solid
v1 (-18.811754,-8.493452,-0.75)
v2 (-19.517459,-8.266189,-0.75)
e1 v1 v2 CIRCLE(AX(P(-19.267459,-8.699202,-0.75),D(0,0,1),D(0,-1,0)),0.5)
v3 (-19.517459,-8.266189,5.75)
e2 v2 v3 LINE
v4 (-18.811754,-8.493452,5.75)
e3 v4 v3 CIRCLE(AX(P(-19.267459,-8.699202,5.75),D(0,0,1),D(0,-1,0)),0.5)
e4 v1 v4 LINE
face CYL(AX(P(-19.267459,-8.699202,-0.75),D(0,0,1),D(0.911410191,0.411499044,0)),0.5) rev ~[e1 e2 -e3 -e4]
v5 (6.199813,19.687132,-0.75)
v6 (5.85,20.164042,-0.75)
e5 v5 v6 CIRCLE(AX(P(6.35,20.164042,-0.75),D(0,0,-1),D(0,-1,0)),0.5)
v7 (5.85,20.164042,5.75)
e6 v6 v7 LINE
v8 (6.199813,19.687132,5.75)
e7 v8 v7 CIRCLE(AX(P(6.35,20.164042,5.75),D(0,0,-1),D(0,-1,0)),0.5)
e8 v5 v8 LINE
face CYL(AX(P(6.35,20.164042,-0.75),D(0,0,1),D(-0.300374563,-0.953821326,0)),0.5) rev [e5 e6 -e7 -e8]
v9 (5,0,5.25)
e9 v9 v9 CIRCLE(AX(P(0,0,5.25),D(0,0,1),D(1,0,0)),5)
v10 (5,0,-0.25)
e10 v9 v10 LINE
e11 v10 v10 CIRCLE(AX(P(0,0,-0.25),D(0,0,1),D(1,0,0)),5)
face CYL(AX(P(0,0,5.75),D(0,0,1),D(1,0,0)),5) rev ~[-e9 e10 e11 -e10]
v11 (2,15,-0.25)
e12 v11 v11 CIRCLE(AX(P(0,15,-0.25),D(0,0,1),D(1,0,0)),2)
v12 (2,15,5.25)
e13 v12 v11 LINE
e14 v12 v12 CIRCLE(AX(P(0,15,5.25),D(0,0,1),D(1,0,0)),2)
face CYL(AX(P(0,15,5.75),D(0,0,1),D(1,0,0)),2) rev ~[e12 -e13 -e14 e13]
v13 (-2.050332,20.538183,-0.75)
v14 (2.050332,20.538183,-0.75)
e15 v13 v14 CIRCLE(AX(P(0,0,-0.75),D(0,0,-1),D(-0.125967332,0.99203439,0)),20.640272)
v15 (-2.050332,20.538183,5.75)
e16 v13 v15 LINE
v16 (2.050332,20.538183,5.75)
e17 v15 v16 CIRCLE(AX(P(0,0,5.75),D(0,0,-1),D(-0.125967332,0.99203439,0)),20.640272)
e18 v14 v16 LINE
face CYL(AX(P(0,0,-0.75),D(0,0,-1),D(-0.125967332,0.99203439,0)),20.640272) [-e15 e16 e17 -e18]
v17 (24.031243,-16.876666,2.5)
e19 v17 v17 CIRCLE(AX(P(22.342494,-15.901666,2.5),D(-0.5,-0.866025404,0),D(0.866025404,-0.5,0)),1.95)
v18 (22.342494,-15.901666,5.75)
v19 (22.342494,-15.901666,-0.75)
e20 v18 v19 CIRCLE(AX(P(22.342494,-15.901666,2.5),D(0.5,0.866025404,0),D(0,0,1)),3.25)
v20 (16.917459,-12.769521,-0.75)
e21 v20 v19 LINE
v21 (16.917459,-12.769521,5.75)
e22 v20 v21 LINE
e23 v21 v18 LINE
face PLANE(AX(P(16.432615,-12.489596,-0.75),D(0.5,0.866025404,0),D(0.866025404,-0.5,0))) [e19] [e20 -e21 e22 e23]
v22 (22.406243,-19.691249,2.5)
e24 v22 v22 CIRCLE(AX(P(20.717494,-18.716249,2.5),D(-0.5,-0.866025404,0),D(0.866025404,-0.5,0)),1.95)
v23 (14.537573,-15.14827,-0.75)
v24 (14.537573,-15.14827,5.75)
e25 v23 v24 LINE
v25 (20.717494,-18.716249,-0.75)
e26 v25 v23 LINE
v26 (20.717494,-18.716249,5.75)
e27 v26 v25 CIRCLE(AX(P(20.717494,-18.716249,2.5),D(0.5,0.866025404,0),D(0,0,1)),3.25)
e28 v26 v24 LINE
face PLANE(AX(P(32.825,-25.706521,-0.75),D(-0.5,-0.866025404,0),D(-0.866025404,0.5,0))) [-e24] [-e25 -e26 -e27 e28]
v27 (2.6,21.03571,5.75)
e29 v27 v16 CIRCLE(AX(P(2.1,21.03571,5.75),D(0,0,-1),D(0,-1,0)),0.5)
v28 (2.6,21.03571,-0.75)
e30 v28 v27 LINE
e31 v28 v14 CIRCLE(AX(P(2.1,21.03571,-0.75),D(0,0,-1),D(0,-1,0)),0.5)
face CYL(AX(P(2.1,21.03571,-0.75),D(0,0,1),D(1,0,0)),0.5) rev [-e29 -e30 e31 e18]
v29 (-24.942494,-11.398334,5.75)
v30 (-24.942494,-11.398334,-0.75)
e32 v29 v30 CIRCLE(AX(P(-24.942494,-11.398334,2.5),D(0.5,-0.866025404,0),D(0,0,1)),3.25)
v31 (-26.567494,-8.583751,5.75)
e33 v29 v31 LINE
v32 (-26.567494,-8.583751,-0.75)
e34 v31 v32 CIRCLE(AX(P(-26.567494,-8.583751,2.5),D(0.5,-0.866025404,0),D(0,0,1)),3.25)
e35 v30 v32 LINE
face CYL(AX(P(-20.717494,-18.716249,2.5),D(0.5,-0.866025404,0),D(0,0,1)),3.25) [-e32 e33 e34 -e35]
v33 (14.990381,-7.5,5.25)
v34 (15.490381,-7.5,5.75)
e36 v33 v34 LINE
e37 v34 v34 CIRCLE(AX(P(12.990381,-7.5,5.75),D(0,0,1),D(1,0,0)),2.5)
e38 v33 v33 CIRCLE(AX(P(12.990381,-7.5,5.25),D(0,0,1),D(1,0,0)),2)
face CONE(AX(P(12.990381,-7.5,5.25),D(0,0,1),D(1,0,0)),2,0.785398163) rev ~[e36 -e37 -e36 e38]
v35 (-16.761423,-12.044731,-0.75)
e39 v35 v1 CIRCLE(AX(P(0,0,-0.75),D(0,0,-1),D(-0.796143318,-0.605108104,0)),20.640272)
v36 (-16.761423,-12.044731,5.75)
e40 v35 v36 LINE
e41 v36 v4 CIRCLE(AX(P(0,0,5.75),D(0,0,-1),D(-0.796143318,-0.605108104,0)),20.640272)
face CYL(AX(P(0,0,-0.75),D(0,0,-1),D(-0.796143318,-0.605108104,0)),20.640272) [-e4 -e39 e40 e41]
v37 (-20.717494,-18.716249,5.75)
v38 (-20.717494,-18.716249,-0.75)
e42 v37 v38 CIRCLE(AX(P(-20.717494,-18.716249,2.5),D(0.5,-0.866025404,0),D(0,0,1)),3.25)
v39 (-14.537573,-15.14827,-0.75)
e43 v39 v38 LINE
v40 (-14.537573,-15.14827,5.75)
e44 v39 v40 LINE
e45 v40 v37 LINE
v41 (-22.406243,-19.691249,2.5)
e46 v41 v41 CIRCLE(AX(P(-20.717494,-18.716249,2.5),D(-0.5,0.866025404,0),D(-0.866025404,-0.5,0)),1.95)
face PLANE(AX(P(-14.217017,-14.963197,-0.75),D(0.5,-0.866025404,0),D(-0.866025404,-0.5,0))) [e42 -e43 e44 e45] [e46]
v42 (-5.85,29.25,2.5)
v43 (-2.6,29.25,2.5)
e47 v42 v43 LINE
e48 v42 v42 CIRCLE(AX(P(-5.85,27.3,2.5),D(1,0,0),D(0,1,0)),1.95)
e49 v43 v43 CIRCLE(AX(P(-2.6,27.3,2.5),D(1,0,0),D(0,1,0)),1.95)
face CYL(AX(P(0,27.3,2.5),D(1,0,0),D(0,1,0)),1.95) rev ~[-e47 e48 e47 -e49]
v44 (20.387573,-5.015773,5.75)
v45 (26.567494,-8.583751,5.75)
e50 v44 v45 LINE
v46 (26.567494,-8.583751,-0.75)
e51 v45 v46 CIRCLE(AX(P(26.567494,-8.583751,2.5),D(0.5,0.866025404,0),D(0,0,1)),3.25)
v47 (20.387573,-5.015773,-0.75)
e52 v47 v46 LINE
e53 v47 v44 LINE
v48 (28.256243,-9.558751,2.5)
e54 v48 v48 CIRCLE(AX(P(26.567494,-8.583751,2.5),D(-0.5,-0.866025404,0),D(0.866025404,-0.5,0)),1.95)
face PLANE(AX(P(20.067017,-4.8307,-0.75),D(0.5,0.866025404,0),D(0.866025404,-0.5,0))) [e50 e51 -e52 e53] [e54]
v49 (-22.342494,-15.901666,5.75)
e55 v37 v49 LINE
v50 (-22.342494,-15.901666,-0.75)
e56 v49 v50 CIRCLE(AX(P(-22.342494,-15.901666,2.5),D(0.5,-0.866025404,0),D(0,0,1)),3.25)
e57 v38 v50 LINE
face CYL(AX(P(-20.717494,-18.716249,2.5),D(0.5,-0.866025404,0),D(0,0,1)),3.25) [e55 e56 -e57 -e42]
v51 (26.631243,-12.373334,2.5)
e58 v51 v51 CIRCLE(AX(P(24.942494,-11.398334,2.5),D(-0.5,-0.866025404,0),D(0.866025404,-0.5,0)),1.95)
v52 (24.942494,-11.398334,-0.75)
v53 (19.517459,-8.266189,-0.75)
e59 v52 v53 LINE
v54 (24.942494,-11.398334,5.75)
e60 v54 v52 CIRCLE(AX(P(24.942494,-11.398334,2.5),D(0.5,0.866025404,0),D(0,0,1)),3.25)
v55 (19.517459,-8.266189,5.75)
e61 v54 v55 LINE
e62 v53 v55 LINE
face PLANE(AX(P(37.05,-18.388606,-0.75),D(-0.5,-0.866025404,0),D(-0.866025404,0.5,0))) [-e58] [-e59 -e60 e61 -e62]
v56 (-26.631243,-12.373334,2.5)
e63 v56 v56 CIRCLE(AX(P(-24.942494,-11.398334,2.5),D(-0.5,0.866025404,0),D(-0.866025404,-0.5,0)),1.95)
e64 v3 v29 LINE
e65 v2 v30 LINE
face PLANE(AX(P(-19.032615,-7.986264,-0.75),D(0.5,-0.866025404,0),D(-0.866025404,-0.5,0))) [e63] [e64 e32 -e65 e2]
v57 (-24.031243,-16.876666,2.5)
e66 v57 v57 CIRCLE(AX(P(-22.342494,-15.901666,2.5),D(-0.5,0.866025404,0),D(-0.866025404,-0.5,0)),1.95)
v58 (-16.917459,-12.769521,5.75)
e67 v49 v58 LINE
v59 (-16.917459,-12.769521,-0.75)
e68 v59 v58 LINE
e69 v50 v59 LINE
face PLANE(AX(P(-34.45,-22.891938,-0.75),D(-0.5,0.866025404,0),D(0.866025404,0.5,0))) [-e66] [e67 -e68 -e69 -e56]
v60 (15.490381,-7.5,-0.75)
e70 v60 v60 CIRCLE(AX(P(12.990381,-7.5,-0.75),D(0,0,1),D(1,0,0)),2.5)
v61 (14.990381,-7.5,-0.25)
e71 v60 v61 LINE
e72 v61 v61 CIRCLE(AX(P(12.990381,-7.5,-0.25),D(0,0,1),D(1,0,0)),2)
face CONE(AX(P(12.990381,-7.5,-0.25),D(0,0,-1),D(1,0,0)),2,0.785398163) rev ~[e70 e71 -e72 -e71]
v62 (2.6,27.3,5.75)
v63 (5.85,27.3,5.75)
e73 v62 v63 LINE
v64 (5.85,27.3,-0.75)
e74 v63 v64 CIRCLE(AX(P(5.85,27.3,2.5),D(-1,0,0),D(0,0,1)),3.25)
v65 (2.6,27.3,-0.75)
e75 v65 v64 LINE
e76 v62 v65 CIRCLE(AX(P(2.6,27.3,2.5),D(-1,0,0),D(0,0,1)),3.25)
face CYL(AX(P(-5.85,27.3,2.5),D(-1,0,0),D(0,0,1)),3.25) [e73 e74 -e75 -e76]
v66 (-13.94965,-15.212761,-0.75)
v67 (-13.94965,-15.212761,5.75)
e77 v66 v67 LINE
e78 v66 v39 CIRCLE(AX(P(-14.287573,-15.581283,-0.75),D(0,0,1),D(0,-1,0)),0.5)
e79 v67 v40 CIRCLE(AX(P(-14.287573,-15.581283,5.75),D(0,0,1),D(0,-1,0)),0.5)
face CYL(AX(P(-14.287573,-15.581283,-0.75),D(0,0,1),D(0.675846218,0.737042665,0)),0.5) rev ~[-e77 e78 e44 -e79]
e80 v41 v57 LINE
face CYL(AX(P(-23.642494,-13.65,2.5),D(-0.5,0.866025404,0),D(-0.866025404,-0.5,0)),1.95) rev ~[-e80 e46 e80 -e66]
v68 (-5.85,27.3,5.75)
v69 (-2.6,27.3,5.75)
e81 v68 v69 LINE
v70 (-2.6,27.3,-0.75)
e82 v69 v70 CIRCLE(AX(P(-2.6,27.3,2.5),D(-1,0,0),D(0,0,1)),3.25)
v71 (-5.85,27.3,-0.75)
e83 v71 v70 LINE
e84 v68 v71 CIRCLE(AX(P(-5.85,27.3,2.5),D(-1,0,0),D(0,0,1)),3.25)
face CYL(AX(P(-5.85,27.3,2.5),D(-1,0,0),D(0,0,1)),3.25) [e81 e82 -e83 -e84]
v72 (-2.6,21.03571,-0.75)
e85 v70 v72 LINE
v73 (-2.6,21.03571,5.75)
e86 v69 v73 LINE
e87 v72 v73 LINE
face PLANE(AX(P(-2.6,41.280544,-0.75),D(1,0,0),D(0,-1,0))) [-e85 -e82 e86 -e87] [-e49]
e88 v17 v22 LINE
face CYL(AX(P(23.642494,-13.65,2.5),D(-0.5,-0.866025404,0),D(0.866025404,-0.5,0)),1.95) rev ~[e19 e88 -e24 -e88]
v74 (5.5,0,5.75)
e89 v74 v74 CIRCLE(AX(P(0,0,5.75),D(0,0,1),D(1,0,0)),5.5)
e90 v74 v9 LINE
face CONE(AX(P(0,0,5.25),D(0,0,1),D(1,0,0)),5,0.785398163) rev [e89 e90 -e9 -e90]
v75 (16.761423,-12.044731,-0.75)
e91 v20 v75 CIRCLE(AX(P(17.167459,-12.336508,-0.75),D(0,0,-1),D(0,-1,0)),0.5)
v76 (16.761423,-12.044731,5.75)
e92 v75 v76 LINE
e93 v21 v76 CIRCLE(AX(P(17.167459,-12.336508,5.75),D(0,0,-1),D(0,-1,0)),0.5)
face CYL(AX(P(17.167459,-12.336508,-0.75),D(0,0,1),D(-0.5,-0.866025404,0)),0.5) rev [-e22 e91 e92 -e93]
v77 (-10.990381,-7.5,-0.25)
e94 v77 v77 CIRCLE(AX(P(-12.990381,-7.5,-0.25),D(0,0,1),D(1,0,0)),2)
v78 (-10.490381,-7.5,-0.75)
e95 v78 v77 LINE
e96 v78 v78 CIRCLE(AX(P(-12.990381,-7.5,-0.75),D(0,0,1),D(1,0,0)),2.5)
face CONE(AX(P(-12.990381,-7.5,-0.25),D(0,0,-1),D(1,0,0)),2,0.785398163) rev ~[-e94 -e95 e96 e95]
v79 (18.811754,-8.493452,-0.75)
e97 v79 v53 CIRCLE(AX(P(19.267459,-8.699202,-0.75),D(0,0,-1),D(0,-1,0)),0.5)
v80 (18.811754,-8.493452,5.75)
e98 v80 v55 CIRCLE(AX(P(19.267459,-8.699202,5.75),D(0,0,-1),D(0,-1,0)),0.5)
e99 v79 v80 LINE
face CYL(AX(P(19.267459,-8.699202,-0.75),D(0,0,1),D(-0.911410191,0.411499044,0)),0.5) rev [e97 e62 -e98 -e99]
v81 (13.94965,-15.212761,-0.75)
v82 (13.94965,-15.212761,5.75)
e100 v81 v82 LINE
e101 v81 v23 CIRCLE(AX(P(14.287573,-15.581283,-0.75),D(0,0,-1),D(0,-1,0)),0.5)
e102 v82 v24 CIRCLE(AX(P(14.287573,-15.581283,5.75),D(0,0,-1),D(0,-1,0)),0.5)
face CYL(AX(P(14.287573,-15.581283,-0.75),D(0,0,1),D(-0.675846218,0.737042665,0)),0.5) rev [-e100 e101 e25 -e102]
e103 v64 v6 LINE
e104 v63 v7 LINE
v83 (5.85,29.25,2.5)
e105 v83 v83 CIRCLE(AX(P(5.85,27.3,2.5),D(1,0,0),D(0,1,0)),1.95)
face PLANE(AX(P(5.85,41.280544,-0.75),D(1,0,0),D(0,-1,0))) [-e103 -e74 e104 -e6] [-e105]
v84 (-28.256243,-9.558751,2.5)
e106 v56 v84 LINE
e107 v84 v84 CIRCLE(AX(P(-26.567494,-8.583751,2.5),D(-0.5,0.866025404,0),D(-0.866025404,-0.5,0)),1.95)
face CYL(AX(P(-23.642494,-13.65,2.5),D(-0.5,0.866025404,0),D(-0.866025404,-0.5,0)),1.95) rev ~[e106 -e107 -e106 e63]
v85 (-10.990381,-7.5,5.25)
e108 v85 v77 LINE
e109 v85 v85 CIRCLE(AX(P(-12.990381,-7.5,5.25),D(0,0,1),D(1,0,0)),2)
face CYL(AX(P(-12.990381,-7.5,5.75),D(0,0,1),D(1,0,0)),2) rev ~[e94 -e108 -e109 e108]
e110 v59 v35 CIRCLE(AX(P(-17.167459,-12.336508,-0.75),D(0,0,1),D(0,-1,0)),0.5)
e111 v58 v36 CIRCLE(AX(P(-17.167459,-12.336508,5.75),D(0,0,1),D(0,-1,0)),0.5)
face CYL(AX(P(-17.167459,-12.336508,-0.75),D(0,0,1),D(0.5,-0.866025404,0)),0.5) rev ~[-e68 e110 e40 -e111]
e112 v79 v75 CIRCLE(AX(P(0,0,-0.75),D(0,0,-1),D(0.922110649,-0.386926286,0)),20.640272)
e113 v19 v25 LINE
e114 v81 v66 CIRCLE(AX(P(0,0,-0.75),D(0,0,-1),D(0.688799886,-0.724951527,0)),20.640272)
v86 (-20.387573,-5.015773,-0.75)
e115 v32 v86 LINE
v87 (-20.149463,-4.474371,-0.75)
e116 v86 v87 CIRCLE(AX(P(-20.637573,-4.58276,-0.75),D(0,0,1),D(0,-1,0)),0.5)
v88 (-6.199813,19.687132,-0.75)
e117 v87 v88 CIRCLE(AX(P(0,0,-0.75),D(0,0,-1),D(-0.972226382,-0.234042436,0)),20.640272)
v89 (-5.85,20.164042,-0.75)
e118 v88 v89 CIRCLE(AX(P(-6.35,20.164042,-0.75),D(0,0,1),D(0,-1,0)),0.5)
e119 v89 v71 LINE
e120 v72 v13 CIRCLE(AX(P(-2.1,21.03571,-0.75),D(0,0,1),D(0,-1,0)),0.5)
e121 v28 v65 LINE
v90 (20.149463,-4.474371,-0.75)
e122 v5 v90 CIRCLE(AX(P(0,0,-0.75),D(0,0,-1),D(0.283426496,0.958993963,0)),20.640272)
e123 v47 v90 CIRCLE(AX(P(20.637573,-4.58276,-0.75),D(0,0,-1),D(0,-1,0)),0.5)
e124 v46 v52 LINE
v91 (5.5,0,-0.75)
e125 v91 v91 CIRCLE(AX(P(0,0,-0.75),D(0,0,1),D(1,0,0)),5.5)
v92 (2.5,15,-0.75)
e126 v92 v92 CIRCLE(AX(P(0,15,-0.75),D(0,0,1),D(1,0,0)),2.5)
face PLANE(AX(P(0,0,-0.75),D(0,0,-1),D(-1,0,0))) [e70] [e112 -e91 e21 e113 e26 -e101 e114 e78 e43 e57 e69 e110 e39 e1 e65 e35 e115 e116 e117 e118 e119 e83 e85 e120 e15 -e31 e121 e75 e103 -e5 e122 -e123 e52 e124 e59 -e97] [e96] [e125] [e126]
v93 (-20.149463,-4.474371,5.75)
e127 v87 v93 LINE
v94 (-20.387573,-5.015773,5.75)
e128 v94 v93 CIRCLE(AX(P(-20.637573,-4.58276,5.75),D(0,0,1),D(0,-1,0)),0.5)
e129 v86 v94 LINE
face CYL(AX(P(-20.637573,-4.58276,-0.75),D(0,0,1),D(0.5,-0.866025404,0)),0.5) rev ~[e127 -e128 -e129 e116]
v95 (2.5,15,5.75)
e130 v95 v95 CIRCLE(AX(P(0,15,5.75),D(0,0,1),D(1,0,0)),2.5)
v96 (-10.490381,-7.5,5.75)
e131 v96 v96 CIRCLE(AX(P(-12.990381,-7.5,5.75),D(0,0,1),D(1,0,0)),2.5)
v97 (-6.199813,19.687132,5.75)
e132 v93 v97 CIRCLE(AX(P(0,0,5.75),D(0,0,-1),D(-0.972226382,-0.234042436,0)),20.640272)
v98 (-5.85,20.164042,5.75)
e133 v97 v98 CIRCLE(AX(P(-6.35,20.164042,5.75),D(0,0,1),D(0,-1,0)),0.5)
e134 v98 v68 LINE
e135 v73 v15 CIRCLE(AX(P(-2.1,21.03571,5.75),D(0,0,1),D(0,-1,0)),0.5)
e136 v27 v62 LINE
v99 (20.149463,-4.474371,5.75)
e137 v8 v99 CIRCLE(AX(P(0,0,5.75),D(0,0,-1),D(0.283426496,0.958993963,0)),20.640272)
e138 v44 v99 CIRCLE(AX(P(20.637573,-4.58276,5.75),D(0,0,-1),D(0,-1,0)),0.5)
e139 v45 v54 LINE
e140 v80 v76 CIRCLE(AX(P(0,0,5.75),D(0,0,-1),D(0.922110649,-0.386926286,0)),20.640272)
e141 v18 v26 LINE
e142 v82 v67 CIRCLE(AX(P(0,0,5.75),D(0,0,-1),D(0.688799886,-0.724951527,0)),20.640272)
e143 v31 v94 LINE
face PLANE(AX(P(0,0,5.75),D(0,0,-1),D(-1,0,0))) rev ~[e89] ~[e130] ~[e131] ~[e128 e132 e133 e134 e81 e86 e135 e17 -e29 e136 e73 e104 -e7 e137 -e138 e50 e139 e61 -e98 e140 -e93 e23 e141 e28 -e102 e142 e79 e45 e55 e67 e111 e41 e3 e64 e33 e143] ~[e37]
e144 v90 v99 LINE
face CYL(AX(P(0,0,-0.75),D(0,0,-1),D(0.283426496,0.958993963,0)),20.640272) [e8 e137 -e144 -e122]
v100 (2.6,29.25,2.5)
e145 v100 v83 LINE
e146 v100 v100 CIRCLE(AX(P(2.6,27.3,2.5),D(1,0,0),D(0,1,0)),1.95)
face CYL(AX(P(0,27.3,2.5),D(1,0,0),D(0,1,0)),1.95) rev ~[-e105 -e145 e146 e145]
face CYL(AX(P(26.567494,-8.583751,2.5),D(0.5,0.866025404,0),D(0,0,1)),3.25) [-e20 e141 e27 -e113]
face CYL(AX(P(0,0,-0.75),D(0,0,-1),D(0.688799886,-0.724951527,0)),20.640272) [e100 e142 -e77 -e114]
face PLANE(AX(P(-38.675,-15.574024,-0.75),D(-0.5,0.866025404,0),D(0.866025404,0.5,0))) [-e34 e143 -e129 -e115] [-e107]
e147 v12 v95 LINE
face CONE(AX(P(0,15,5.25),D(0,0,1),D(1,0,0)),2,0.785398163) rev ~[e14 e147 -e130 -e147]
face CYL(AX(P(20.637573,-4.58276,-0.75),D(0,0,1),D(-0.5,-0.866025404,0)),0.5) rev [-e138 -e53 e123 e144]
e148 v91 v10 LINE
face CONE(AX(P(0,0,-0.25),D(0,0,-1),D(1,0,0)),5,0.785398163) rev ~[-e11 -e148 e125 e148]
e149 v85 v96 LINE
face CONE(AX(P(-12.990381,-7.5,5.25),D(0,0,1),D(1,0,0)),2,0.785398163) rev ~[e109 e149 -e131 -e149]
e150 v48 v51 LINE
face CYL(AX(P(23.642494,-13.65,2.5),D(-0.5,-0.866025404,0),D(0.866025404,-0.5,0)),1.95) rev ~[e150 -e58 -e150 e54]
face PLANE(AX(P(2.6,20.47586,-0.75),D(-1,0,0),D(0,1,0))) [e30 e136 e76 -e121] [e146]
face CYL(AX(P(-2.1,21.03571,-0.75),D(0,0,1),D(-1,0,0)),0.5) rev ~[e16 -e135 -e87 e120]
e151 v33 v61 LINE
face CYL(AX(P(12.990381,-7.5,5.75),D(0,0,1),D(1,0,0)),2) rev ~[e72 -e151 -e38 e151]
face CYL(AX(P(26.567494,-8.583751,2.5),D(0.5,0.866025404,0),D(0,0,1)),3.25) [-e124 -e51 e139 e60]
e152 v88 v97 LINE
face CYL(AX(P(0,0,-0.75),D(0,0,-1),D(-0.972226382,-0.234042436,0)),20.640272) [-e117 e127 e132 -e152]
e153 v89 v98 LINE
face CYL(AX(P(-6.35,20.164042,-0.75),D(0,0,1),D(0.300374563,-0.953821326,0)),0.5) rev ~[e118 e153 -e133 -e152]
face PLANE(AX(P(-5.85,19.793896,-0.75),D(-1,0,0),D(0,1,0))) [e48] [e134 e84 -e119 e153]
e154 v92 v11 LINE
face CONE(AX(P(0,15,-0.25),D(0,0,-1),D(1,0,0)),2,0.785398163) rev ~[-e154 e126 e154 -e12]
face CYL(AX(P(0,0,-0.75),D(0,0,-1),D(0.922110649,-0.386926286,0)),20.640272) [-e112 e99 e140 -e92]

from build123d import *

# Parameters (mm, degrees)
BOSS_EXTRUDE1_DEPTH = 5
SKETCH2_R           = 1.5
CUT_EXTRUDE1_DEPTH  = 15.5
CUT_EXTRUDE3_DEPTH  = 27
CIRPATTERN1_COUNT   = 3
CIRPATTERN2_COUNT   = 3
SCALE_RATIO_1_SCALE = 1.3
SKETCH5_R           = 5
CUT_EXTRUDE4_DEPTH  = 10
CHAMFER1_SIZE       = 0.5
SKETCH8_R           = 2
CUT_EXTRUDE5_DEPTH  = 10
CHAMFER2_SIZE       = 0.5
FILLET1_R           = 0.5


with BuildPart() as part:
    # Sketch1 → Boss-Extrude1 (new body)
    with BuildSketch(Plane.XY):
        with BuildLine():
            Line((-26.5, -17.60918321), (-12.640472866, -9.607381488))
            ThreePointArc((-12.640472866, -9.607381488), (-13.75, -7.938566201), (-14.640472866, -6.143279873))
            Line((-14.640472866, -6.143279873), (-28.5, -14.145081595))
            Line((-28.5, -14.145081595), (-29.75, -11.980018086))
            Line((-29.75, -11.980018086), (-15.436166994, -3.715922747))
            ThreePointArc((-15.436166994, -3.715922747), (-13.75, 7.938566201), (-4.5, 15.226074127))
            Line((-4.5, 15.226074127), (-4.5, 31.754264805))
            Line((-4.5, 31.754264805), (-2, 31.754264805))
            Line((-2, 31.754264805), (-2, 15.750661362))
            ThreePointArc((-2, 15.750661362), (0, 15.877132403), (2, 15.750661362))
            Line((2, 15.750661362), (2, 31.754264805))
            Line((2, 31.754264805), (4.5, 31.754264805))
            Line((4.5, 31.754264805), (4.5, 15.226074127))
            ThreePointArc((4.5, 15.226074127), (13.75, 7.938566201), (15.436166994, -3.715922747))
            Line((15.436166994, -3.715922747), (29.75, -11.980018086))
            Line((29.75, -11.980018086), (28.5, -14.145081595))
            Line((28.5, -14.145081595), (14.640472866, -6.143279873))
            ThreePointArc((14.640472866, -6.143279873), (13.75, -7.938566201), (12.640472866, -9.607381488))
            Line((12.640472866, -9.607381488), (26.5, -17.60918321))
            Line((26.5, -17.60918321), (25.25, -19.77424672))
            Line((25.25, -19.77424672), (10.936166994, -11.510151381))
            ThreePointArc((10.936166994, -11.510151381), (0, -15.877132403), (-10.936166994, -11.510151381))
            Line((-10.936166994, -11.510151381), (-25.25, -19.77424672))
            Line((-25.25, -19.77424672), (-26.5, -17.60918321))
        make_face()
    extrude(amount=BOSS_EXTRUDE1_DEPTH)

    # Sketch2 → Cut-Extrude1 (cut, symmetric)
    with BuildSketch(Plane(origin=(0, 0, 0), x_dir=(0, 0, -1), z_dir=(1, 0, 0))):
        with Locations(Location((-2.5, 21, 0), (0, 0, 90))):
            Circle(SKETCH2_R)
    cut_extrude1 = extrude(amount=CUT_EXTRUDE1_DEPTH, both=True, mode=Mode.SUBTRACT)

    # Sketch4 → Cut-Extrude3 (cut)
    with BuildSketch(Plane.ZY.offset(4.5)):
        with BuildLine():
            Line((0, 21), (0, 31.754264805))
            Line((0, 31.754264805), (5, 31.754264805))
            Line((5, 31.754264805), (5, 21))
            ThreePointArc((5, 21), (2.5, 23.5), (0, 21))
        make_face()
    cut_extrude3 = extrude(amount=-CUT_EXTRUDE3_DEPTH, mode=Mode.SUBTRACT)

    # CirPattern1: Cut-Extrude3 ×3 about axis
    cirpattern1_axis = Axis((0, 0, 5), (0, 0, -1))
    for i in range(1, CIRPATTERN1_COUNT):
        add(cut_extrude3.rotate(cirpattern1_axis, i * 360 / CIRPATTERN1_COUNT), mode=Mode.SUBTRACT)

    # CirPattern2: Cut-Extrude1 ×3 about axis
    cirpattern2_axis = Axis((0, 0, 5), (0, 0, -1))
    for i in range(1, CIRPATTERN2_COUNT):
        add(cut_extrude1.rotate(cirpattern2_axis, i * 360 / CIRPATTERN2_COUNT), mode=Mode.SUBTRACT)


with BuildPart() as part_1:
    # Scale ratio 1: scaled about (0, 0, 2.5)
    add(part.part.scale(SCALE_RATIO_1_SCALE).moved(Location((0, 0, -0.75))))

    # Sketch5 → Cut-Extrude4 (cut)
    with BuildSketch(Plane.XY.offset(5.75)):
        Circle(SKETCH5_R)
    extrude(amount=-CUT_EXTRUDE4_DEPTH, mode=Mode.SUBTRACT)

    # Chamfer1
    chamfer1_edges = [part_1.edges().sort_by_distance(p)[0] for p in [
        (-5, 0, -0.75),
        (-5, 0, 5.75),
    ]]
    chamfer(chamfer1_edges, length=CHAMFER1_SIZE)

    # Sketch8 → Cut-Extrude5 (cut)
    with BuildSketch(Plane.XY.offset(5.75)):
        with Locations((0, 15)):
            Circle(SKETCH8_R)
        with Locations((12.990381057, -7.5)):
            Circle(SKETCH8_R)
        with Locations((-12.990381057, -7.5)):
            Circle(SKETCH8_R)
    extrude(amount=-CUT_EXTRUDE5_DEPTH, mode=Mode.SUBTRACT)

    # Chamfer2
    chamfer2_edges = [part_1.edges().sort_by_distance(p)[0] for p in [
        (-2, 15, -0.75),
        (-2, 15, 5.75),
        (10.990381057, -7.5, -0.75),
        (10.990381057, -7.5, 5.75),
        (-14.990381057, -7.5, -0.75),
        (-14.990381057, -7.5, 5.75),
    ]]
    chamfer(chamfer2_edges, length=CHAMFER2_SIZE)

    # Fillet1
    fillet1_edges = [part_1.edges().sort_by_distance(p)[0] for p in [
        (-16.432614725, -12.489595935, 2.5),
        (-19.032614725, -7.986263835, 2.5),
        (-20.067017093, -4.830699571, 2.5),
        (-5.85, 19.793896366, 2.5),
        (-2.6, 20.47585977, 2.5),
        (2.6, 20.47585977, 2.5),
        (5.85, 19.793896366, 2.5),
        (20.067017093, -4.830699571, 2.5),
        (19.032614725, -7.986263835, 2.5),
        (16.432614725, -12.489595935, 2.5),
        (14.217017093, -14.963196795, 2.5),
        (-14.217017093, -14.963196795, 2.5),
    ]]
    fillet(fillet1_edges, radius=FILLET1_R)


solid = part_1.part
